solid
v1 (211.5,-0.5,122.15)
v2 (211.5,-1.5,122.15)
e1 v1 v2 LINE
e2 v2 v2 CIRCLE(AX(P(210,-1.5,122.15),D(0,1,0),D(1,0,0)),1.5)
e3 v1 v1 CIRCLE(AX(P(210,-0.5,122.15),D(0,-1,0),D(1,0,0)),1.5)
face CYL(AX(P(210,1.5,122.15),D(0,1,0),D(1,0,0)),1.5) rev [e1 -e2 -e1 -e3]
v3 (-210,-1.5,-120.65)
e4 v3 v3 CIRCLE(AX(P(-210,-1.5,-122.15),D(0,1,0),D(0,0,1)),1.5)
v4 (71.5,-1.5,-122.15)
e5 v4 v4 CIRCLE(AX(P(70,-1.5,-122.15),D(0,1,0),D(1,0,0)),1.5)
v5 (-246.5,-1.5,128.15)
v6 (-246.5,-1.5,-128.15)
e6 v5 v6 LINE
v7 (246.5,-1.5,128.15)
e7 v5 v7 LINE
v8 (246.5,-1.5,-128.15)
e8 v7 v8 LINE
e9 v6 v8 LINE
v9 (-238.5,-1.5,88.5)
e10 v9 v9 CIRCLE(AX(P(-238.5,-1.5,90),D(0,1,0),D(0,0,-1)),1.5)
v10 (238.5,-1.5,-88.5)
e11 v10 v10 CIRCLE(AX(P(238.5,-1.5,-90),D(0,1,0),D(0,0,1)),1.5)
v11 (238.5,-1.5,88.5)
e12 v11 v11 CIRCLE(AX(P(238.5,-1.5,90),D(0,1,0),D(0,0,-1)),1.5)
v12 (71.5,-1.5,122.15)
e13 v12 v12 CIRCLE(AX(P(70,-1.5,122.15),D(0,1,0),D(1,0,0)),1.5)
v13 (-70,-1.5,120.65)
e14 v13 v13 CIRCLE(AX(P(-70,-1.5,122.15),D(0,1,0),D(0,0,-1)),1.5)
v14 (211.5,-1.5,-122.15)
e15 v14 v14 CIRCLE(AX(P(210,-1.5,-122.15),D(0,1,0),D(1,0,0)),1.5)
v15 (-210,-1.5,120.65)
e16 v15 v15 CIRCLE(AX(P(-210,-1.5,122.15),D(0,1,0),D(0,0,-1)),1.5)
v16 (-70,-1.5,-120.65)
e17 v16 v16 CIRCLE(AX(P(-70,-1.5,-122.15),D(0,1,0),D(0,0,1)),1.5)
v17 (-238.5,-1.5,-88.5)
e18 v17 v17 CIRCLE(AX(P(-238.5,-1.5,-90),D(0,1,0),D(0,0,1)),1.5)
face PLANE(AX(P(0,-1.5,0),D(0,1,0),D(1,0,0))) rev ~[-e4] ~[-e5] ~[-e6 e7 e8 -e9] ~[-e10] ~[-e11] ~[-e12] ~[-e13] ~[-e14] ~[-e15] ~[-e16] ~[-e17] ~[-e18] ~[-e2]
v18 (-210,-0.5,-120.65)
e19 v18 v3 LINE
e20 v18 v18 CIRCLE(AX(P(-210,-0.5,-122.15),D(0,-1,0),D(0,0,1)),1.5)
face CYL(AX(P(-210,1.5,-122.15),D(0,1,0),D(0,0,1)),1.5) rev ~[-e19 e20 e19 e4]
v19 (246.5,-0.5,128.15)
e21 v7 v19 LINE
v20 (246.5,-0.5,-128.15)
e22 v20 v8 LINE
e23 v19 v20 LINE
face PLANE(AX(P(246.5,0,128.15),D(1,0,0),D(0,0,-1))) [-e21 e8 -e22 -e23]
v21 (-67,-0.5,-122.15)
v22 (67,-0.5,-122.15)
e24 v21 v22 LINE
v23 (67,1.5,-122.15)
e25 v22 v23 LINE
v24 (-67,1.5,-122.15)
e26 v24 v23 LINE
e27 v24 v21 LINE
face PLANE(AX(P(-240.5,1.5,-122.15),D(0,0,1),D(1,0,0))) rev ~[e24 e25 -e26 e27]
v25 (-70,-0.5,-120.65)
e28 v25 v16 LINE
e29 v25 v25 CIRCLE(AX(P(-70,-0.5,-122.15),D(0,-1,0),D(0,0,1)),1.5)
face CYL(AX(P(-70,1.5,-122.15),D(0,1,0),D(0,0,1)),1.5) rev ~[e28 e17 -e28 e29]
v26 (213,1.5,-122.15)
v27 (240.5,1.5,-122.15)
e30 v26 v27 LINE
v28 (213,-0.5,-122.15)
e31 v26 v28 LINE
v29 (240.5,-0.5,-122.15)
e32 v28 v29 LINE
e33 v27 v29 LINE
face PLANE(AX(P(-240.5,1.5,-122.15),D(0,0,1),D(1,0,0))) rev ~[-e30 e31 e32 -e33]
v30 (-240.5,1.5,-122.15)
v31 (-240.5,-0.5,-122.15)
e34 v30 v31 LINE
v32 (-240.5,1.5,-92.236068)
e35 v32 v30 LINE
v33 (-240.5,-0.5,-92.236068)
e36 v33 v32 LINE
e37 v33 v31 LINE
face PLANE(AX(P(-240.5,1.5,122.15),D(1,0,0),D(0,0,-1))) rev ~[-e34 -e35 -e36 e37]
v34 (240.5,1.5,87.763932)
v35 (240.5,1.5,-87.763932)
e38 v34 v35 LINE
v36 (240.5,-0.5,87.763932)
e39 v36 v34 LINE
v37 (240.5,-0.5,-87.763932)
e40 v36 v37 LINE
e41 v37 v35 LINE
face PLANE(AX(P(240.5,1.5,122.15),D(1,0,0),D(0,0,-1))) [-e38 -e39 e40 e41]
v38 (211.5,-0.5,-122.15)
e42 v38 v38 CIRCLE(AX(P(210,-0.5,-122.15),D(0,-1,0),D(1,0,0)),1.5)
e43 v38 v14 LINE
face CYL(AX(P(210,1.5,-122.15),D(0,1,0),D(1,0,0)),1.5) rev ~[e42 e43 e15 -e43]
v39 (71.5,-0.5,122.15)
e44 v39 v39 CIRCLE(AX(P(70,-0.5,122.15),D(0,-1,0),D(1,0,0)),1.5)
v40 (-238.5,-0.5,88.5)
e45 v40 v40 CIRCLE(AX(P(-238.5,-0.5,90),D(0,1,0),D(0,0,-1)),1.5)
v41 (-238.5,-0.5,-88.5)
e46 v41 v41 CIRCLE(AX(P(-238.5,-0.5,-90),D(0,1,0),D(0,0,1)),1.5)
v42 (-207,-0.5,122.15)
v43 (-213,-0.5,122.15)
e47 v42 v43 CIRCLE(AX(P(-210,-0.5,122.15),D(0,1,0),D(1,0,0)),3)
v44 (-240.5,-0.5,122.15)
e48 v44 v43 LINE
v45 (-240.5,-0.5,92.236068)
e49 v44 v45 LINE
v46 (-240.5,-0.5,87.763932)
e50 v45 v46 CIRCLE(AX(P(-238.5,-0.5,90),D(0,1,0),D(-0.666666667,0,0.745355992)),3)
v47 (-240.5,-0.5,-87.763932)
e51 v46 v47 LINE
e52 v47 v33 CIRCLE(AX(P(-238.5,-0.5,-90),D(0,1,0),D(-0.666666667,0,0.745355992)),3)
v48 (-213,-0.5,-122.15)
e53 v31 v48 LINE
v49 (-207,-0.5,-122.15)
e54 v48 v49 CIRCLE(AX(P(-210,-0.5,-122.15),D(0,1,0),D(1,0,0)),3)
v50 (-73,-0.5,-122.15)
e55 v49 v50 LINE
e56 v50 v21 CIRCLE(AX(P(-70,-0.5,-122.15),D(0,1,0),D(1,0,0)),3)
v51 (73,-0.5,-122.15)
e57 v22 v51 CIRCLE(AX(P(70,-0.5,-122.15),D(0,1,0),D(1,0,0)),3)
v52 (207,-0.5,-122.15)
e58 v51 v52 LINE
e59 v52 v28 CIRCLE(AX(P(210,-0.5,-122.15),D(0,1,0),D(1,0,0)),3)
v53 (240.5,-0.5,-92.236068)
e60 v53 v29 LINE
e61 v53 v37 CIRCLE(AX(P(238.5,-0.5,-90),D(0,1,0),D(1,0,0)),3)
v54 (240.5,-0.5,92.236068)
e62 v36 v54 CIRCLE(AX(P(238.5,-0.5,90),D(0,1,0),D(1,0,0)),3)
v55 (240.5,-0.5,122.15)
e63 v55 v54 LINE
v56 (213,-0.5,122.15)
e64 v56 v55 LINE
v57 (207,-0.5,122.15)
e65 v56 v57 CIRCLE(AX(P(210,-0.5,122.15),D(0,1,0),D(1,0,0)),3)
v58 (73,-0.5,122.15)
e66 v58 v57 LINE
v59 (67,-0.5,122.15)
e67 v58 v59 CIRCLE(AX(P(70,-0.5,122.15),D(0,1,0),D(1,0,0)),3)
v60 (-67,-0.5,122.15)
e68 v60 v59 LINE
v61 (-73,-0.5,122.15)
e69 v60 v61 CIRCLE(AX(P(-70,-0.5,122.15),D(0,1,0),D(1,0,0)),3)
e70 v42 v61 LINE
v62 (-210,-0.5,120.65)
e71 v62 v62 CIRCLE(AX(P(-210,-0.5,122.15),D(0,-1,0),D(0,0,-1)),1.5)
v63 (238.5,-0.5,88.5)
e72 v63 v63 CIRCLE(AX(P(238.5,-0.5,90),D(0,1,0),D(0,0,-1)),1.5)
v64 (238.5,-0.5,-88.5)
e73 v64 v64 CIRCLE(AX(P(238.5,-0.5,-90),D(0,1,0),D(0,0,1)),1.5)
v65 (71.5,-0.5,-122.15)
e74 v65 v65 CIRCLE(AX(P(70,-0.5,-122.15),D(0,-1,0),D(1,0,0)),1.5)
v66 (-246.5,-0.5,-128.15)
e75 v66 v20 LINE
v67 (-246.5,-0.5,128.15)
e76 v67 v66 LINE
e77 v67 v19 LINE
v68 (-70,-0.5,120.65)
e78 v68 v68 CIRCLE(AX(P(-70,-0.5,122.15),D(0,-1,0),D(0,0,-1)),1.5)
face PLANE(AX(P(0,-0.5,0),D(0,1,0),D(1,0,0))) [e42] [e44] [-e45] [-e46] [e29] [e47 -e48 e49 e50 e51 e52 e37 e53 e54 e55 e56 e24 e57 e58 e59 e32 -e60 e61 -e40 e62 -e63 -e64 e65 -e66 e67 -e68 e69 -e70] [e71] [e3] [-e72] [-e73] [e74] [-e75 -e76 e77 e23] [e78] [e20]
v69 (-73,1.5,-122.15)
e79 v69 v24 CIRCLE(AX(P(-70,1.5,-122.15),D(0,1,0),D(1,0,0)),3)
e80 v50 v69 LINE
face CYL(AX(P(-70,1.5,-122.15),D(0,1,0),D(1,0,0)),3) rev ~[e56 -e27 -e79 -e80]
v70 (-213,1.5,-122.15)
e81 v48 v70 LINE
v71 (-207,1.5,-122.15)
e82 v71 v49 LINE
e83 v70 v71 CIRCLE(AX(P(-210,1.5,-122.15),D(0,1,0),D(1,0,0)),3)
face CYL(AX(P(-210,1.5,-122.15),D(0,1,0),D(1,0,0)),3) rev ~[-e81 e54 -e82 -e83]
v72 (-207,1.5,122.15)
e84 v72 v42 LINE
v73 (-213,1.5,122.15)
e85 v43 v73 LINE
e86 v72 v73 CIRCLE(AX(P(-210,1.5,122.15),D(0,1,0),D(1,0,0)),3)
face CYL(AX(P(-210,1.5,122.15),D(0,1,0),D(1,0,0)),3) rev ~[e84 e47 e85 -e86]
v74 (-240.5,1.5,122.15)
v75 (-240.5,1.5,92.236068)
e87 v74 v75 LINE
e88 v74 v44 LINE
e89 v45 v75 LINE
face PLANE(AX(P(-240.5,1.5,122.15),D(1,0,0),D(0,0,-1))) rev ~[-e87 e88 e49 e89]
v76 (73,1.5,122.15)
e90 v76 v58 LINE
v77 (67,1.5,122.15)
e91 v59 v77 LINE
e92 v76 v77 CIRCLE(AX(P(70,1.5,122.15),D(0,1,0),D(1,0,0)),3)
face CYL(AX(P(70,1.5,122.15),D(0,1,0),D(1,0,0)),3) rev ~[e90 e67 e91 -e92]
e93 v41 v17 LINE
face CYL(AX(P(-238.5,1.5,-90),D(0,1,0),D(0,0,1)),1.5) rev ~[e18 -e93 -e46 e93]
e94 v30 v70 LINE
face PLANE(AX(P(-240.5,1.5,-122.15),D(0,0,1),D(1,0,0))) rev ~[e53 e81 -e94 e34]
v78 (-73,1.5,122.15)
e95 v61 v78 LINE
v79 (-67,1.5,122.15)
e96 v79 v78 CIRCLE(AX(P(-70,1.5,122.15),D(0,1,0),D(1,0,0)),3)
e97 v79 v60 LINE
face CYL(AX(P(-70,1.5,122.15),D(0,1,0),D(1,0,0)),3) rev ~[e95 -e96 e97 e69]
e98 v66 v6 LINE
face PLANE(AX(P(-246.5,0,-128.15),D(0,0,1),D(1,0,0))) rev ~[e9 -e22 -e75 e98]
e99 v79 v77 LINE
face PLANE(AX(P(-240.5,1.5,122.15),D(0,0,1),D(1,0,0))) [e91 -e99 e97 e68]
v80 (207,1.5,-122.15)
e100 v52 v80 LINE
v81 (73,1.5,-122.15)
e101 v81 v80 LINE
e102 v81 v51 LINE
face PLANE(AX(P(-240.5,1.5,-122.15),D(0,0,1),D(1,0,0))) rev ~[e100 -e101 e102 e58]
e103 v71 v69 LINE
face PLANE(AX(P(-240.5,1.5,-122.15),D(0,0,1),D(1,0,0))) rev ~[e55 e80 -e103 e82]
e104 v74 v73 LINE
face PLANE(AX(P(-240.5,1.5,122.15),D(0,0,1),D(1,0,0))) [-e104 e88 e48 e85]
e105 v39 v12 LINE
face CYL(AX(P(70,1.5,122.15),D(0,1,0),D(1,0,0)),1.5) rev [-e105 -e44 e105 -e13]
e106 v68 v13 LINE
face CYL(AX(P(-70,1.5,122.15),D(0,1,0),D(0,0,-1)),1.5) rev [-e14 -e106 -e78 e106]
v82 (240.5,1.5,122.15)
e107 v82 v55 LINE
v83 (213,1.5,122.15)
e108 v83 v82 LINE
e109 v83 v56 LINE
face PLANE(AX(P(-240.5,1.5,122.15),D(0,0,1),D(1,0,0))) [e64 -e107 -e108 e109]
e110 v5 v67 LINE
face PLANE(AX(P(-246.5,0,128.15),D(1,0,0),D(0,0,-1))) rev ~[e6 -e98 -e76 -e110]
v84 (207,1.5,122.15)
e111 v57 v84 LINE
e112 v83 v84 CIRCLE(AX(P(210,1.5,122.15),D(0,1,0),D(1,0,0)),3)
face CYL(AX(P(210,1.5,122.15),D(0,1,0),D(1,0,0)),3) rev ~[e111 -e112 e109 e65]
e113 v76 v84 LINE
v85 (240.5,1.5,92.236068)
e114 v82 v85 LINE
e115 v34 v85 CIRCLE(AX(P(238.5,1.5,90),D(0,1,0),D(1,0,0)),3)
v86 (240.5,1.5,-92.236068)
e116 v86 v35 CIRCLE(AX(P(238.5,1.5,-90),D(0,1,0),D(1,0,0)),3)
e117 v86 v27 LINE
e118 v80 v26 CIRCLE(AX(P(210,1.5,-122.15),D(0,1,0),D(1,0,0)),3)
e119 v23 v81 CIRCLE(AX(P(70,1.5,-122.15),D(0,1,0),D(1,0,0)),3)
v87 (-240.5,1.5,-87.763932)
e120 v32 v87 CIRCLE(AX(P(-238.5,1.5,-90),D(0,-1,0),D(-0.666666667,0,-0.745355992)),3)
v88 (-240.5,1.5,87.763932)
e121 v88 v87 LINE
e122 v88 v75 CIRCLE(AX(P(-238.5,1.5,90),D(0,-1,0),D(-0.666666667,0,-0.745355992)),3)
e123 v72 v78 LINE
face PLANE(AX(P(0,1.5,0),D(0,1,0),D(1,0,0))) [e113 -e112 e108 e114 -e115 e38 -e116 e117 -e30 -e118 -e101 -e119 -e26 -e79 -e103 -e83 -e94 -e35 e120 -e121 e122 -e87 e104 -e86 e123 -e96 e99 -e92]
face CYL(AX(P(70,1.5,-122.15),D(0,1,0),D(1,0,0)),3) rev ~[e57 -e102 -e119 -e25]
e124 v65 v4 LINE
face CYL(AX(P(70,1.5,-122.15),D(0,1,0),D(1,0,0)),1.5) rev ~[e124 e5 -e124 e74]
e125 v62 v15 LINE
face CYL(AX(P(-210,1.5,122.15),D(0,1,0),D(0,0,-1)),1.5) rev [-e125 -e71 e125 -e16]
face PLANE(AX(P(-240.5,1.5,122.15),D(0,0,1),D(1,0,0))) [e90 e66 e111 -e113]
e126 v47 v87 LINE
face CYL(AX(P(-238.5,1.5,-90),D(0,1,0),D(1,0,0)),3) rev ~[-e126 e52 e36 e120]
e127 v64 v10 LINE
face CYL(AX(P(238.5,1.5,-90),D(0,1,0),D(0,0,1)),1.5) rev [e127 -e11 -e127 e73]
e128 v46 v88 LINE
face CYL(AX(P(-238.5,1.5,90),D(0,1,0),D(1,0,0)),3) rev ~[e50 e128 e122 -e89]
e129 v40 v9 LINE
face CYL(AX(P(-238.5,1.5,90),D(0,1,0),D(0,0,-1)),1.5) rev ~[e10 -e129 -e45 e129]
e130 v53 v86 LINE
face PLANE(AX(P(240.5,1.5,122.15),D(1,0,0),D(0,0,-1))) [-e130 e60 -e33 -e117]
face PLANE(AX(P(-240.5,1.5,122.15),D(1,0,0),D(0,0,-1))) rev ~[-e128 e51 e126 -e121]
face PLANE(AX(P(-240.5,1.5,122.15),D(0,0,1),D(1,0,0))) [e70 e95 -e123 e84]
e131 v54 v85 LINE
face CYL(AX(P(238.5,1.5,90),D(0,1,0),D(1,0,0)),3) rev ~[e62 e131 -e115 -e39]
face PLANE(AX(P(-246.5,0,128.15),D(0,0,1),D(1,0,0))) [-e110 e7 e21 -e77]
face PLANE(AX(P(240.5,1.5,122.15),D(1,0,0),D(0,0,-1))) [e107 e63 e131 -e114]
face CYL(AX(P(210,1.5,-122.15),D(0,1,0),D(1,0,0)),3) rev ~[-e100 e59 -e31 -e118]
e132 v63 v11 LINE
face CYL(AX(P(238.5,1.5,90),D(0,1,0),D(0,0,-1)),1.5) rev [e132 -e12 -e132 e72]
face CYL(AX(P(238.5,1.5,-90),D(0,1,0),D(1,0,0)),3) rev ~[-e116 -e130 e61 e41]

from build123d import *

# Parameters (mm, degrees)
SKETCH1_W           = 493
SKETCH1_H           = 256.3
BOSS_EXTRUDE1_DEPTH = 1.5
SKETCH2_W           = 493
SKETCH2_H           = 256.3
SKETCH2_W_2         = 481
SKETCH2_H_2         = 244.3
CUT_EXTRUDE1_DEPTH  = 2
SKETCH3_R           = 1.5
CUT_EXTRUDE2_DEPTH  = 278.83749297
SKETCH4_R           = 1.5
CUT_EXTRUDE3_DEPTH  = 278.83749297
SKETCH5_R           = 3
CUT_EXTRUDE4_DEPTH  = 2


with BuildPart() as part:
    # Sketch1 → Boss-Extrude1 (new, symmetric)
    with BuildSketch(Plane(origin=(0, 0, 0), x_dir=(1, 0, 0), z_dir=(0, 1, 0))):
        Rectangle(SKETCH1_W, SKETCH1_H)
    extrude(amount=BOSS_EXTRUDE1_DEPTH, both=True)

    # Sketch2 → Cut-Extrude1 (cut)
    with BuildSketch(Plane(origin=(0, 1.5, 0), x_dir=(1, 0, 0), z_dir=(0, 1, 0))):
        Rectangle(SKETCH2_W, SKETCH2_H)
        Rectangle(SKETCH2_W_2, SKETCH2_H_2, mode=Mode.SUBTRACT)
    extrude(amount=-CUT_EXTRUDE1_DEPTH, mode=Mode.SUBTRACT)

    # Sketch3 → Cut-Extrude2 (cut, through all)
    with BuildSketch(Plane(origin=(0, 1.5, 0), x_dir=(1, 0, 0), z_dir=(0, 1, 0))):
        with Locations(Location((-70, 122.15, 0), (0, 0, 270))):
            Circle(SKETCH3_R)
        with Locations(Location((-210, 122.15, 0), (0, 0, 270))):
            Circle(SKETCH3_R)
        with Locations((70, 122.15)):
            Circle(SKETCH3_R)
        with Locations((210, 122.15)):
            Circle(SKETCH3_R)
    cut_extrude2 = extrude(amount=-CUT_EXTRUDE2_DEPTH, mode=Mode.SUBTRACT)

    # Mirror1: Cut-Extrude2 across plane
    add(cut_extrude2.mirror(Plane.XY), mode=Mode.SUBTRACT)

    # Sketch4 → Cut-Extrude3 (cut, through all)
    with BuildSketch(Plane(origin=(0, 1.5, 0), x_dir=(1, 0, 0), z_dir=(0, 1, 0))):
        with Locations(Location((-238.5, 90, 0), (0, 0, 270))):
            Circle(SKETCH4_R)
        with Locations(Location((-238.5, -90, 0), (0, 0, 90))):
            Circle(SKETCH4_R)
    cut_extrude3 = extrude(amount=-CUT_EXTRUDE3_DEPTH, mode=Mode.SUBTRACT)

    # Mirror2: Cut-Extrude3 across plane
    add(cut_extrude3.mirror(Plane(origin=(0, 0, 0), x_dir=(0, 0, 1), z_dir=(1, 0, 0))), mode=Mode.SUBTRACT)

    # Sketch5 → Cut-Extrude4 (cut)
    with BuildSketch(Plane(origin=(0, 1.5, 0), x_dir=(1, 0, 0), z_dir=(0, 1, 0))):
        with Locations((-210, 122.15)):
            Circle(SKETCH5_R)
        with Locations((-70, 122.15)):
            Circle(SKETCH5_R)
        with Locations((70, 122.15)):
            Circle(SKETCH5_R)
        with Locations((210, 122.15)):
            Circle(SKETCH5_R)
        with Locations((238.5, 90)):
            Circle(SKETCH5_R)
        with Locations((238.5, -90)):
            Circle(SKETCH5_R)
        with Locations((210, -122.15)):
            Circle(SKETCH5_R)
        with Locations((70, -122.15)):
            Circle(SKETCH5_R)
        with Locations((-70, -122.15)):
            Circle(SKETCH5_R)
        with Locations((-210, -122.15)):
            Circle(SKETCH5_R)
        with Locations((-238.5, -90)):
            Circle(SKETCH5_R)
        with Locations((-238.5, 90)):
            Circle(SKETCH5_R)
    extrude(amount=-CUT_EXTRUDE4_DEPTH, mode=Mode.SUBTRACT)


solid = part.part
